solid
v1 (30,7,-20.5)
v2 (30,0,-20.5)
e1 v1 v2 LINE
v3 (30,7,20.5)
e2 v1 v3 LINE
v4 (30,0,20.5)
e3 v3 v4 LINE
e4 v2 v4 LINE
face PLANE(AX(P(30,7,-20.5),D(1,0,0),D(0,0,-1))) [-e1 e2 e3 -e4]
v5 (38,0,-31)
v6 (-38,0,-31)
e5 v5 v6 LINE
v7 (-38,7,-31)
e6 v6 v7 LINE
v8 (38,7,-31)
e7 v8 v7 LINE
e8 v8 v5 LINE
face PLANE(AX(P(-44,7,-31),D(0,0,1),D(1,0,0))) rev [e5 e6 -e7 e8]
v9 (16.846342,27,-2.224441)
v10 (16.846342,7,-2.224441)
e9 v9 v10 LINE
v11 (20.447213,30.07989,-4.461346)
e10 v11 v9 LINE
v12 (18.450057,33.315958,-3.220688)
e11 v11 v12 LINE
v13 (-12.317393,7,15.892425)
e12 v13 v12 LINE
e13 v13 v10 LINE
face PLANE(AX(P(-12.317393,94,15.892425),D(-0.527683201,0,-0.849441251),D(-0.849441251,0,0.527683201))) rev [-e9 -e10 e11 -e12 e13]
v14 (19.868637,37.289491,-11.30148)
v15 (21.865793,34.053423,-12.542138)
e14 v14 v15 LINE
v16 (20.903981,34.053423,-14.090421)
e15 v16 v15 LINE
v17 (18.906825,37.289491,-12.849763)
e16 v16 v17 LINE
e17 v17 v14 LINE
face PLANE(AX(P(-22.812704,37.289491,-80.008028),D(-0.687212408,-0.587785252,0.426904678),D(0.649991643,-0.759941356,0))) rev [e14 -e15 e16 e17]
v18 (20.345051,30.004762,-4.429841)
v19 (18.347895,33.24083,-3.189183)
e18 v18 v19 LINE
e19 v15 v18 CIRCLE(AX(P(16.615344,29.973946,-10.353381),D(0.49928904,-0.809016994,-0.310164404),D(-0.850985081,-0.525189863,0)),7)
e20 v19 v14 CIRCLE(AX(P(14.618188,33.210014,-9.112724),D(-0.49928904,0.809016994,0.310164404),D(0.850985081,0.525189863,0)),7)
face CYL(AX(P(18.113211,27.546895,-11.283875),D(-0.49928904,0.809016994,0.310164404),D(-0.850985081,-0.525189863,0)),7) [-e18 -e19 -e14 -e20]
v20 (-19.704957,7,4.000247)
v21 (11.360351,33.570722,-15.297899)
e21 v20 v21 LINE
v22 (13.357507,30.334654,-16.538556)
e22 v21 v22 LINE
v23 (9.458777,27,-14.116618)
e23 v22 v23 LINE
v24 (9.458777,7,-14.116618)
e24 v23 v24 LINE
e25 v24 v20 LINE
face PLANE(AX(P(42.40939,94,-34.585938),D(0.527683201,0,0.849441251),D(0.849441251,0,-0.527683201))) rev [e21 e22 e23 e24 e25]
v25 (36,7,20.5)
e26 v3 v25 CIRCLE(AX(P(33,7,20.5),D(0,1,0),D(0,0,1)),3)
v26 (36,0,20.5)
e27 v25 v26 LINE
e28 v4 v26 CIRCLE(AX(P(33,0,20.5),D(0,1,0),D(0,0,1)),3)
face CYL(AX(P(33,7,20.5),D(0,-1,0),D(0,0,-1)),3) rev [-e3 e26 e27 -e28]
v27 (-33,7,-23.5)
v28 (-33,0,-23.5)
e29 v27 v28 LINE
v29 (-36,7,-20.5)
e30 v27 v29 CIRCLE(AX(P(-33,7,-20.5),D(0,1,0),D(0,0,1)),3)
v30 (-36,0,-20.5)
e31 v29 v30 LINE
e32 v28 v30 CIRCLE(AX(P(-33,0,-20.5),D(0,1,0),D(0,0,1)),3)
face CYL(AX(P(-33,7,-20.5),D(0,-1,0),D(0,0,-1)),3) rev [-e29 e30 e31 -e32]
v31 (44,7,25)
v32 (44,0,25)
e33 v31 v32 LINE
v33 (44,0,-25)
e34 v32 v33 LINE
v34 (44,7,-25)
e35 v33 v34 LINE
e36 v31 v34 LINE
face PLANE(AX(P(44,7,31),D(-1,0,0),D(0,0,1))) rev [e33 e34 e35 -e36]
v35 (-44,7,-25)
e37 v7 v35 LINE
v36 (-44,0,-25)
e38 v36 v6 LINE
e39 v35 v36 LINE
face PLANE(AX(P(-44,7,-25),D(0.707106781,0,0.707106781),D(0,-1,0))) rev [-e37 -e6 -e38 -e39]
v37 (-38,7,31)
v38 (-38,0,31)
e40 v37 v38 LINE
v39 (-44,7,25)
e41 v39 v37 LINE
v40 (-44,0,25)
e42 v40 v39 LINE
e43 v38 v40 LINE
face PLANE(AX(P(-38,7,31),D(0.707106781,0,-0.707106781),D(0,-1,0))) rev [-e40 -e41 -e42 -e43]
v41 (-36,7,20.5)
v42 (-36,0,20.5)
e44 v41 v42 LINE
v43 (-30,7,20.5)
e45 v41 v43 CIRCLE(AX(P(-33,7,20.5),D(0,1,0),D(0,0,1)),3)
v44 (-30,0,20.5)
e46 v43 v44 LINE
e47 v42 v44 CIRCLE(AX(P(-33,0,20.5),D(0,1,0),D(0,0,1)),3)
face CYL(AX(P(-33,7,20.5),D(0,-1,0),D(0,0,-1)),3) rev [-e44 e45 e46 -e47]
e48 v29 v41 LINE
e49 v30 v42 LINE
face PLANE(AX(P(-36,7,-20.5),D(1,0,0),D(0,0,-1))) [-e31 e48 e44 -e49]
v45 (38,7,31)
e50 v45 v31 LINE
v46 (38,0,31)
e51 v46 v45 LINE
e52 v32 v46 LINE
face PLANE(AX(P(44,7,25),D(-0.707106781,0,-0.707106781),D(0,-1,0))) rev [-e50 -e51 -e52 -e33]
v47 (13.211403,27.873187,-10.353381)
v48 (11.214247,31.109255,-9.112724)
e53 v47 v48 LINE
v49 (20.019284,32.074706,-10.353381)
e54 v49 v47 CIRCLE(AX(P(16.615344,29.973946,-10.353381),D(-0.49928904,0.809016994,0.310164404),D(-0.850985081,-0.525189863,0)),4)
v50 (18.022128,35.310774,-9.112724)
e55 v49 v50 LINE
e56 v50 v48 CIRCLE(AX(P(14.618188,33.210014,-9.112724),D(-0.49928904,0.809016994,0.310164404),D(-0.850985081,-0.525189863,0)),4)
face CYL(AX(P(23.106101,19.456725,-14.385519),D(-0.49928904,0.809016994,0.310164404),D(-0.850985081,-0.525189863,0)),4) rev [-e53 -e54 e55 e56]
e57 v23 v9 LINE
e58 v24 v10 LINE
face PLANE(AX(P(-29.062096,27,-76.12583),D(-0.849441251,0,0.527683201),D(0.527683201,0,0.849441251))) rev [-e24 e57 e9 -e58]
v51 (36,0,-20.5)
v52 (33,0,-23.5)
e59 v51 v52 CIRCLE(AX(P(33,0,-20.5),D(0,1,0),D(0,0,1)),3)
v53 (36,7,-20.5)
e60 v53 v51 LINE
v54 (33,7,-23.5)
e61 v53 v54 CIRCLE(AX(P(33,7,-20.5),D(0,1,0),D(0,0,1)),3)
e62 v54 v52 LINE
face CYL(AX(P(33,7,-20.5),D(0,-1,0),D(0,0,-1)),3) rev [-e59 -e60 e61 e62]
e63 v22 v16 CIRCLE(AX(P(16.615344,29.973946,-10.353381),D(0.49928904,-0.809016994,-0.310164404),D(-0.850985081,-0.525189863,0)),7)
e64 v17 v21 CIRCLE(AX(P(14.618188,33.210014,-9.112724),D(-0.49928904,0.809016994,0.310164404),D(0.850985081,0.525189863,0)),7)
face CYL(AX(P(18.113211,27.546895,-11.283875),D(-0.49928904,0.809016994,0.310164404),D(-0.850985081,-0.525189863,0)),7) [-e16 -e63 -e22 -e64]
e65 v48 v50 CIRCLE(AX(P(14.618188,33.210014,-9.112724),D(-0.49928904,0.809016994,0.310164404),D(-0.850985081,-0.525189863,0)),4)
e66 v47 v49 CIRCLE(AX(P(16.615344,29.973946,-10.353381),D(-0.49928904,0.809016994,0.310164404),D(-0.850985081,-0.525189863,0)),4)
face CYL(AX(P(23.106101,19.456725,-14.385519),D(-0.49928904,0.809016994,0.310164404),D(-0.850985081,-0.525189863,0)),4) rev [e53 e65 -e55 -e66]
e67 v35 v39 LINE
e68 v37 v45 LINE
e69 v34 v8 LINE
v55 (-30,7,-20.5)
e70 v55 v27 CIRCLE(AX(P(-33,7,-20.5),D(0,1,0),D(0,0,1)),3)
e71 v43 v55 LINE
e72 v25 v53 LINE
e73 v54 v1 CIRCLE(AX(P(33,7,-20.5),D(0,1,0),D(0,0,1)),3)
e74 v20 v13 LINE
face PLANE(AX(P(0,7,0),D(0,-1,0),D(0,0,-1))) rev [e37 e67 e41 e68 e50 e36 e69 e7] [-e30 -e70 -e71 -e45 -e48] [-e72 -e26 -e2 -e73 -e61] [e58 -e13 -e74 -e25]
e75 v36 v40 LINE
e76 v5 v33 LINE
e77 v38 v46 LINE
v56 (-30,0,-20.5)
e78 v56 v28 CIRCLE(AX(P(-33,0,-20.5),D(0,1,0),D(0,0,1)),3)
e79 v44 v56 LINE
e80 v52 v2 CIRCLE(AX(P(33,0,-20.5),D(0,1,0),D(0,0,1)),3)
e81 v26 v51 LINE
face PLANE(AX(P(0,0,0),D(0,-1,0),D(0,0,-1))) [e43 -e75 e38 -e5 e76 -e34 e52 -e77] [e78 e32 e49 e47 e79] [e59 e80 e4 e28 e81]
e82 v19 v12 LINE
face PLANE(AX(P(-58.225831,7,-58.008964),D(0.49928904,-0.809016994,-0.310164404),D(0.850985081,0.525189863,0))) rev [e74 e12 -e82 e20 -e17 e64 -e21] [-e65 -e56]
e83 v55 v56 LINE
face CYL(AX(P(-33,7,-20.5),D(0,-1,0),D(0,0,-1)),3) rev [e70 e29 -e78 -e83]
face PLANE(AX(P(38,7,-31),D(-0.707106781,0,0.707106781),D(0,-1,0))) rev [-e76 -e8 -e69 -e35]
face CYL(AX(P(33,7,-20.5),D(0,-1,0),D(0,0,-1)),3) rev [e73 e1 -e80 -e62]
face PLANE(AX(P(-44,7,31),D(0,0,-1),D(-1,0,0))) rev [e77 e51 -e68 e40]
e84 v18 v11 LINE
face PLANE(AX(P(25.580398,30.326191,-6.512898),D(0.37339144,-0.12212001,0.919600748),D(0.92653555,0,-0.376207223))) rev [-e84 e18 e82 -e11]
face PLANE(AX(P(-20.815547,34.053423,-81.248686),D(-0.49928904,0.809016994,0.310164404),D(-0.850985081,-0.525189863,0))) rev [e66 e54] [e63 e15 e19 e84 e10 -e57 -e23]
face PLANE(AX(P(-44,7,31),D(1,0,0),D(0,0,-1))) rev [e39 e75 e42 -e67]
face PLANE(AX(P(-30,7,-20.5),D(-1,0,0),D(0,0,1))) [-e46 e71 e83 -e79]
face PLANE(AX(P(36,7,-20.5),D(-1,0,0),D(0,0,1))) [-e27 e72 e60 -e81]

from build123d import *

# Parameters (mm, degrees)
BASE_PLATE_PROFILE_W        = 88
BASE_PLATE_PROFILE_H        = 62
BASE_PLATE_88X62X7_DEPTH    = 7
PLATE_EDGE_CHAMFER_6MM_SIZE = 6
LIFTING_LUG_DEPTH           = 87
LUG_TAPER_CUT_DEPTH         = 87
LUG_TRIM_CUT_DEPTH          = 7
LUG_EYE_HOLE_PROFILE_R      = 4
LUG_EYE_HOLE_DEPTH          = 17


with BuildPart() as part:
    # Base Plate Profile → Base Plate 88x62x7 (new body)
    with BuildSketch(Plane(origin=(0, 0, 0), x_dir=(1, 0, 0), z_dir=(0, 1, 0))):
        Rectangle(BASE_PLATE_PROFILE_W, BASE_PLATE_PROFILE_H)
        with BuildLine():
            Line((-30, 20.5), (-30, -20.5))
            ThreePointArc((-30, -20.5), (-33, -23.5), (-36, -20.5))
            Line((-36, -20.5), (-36, 20.5))
            ThreePointArc((-36, 20.5), (-33, 23.5), (-30, 20.5))
        make_face(mode=Mode.SUBTRACT)
        with BuildLine():
            Line((36, 20.5), (36, -20.5))
            ThreePointArc((36, -20.5), (33, -23.5), (30, -20.5))
            Line((30, -20.5), (30, 20.5))
            ThreePointArc((30, 20.5), (33, 23.5), (36, 20.5))
        make_face(mode=Mode.SUBTRACT)
    extrude(amount=BASE_PLATE_88X62X7_DEPTH)

    # Plate Edge Chamfer 6mm
    plate_edge_chamfer_6mm_edges = [part.edges().sort_by_distance(p)[0] for p in [
        (44, 3.5, 31),
        (-44, 3.5, 31),
        (-44, 3.5, -31),
        (44, 3.5, -31),
    ]]
    chamfer(plate_edge_chamfer_6mm_edges, length=PLATE_EDGE_CHAMFER_6MM_SIZE)

    # Lug Profile → Lifting Lug (add)
    with BuildSketch(Plane(origin=(0, 7, 0), x_dir=(1, 0, 0), z_dir=(0, 1, 0))):
        Polygon((-19.704957389, -4.000247215), (-12.317392569, -15.892424729), (49.796954416, 22.693760519), (42.409389597, 34.585938034), align=None)
    extrude(amount=LIFTING_LUG_DEPTH)

    # Lug Taper Cut Profile → Lug Taper Cut (cut)
    with BuildSketch(Plane(origin=(3.69378241, 0, 5.946088757), x_dir=(0.849441251034907, 0, -0.527683201400473), z_dir=(0.527683201400473, 0, 0.8494412510349071))):
        Polygon((-18.849066913, 7), (22.840840887, 37.289491005), (25.191981896, 34.053423028), (15.483777963, 27), (15.483777963, 7), (61.160327949, 7), (67.88344363, 13.003001153), (104.454353656, 45.656792269), (102.884273853, 93.151706309), (-3.096112848, 106.69364461), (-91.21684179, 88.04894695), align=None)
    extrude(amount=-LUG_TAPER_CUT_DEPTH, mode=Mode.SUBTRACT)

    # Lug Trim Profile → Lug Trim Cut (cut)
    with BuildSketch(Plane(origin=(-8.359258135, 13.544823437, 5.192872478), x_dir=(0.8664354877824213, 0.46620126275894425, 0.17873423878262307), z_dir=(-0.4992890400471833, 0.8090169943749503, 0.31016440366567466))):
        with BuildLine():
            Line((21.785997787, 25.554185682), (25.412738519, 37.418943579))
            Line((25.412738519, 37.418943579), (44.862853062, 15.660355845))
            Line((44.862853062, 15.660355845), (35.13779579, 16.937383568))
            Line((35.13779579, 16.937383568), (30.824168068, 14.877305743))
            ThreePointArc((30.824168068, 14.877305743), (31.862256086, 24.919992419), (21.785997787, 25.554185682))
        make_face()
    extrude(amount=-LUG_TRIM_CUT_DEPTH, mode=Mode.SUBTRACT)

    # Lug Eye Hole Profile → Lug Eye Hole (cut)
    with BuildSketch(Plane(origin=(-8.359258135, 13.544823437, 5.192872478), x_dir=(0.8664354877824213, 0.46620126275894425, 0.17873423878262307), z_dir=(-0.4992890400471833, 0.8090169943749503, 0.31016440366567466))):
        with Locations(Location((26.519511391, 20.397263251, 0), (0, 0, 190.836448225))):
            Circle(LUG_EYE_HOLE_PROFILE_R)
    extrude(amount=-LUG_EYE_HOLE_DEPTH, mode=Mode.SUBTRACT)


solid = part.part
